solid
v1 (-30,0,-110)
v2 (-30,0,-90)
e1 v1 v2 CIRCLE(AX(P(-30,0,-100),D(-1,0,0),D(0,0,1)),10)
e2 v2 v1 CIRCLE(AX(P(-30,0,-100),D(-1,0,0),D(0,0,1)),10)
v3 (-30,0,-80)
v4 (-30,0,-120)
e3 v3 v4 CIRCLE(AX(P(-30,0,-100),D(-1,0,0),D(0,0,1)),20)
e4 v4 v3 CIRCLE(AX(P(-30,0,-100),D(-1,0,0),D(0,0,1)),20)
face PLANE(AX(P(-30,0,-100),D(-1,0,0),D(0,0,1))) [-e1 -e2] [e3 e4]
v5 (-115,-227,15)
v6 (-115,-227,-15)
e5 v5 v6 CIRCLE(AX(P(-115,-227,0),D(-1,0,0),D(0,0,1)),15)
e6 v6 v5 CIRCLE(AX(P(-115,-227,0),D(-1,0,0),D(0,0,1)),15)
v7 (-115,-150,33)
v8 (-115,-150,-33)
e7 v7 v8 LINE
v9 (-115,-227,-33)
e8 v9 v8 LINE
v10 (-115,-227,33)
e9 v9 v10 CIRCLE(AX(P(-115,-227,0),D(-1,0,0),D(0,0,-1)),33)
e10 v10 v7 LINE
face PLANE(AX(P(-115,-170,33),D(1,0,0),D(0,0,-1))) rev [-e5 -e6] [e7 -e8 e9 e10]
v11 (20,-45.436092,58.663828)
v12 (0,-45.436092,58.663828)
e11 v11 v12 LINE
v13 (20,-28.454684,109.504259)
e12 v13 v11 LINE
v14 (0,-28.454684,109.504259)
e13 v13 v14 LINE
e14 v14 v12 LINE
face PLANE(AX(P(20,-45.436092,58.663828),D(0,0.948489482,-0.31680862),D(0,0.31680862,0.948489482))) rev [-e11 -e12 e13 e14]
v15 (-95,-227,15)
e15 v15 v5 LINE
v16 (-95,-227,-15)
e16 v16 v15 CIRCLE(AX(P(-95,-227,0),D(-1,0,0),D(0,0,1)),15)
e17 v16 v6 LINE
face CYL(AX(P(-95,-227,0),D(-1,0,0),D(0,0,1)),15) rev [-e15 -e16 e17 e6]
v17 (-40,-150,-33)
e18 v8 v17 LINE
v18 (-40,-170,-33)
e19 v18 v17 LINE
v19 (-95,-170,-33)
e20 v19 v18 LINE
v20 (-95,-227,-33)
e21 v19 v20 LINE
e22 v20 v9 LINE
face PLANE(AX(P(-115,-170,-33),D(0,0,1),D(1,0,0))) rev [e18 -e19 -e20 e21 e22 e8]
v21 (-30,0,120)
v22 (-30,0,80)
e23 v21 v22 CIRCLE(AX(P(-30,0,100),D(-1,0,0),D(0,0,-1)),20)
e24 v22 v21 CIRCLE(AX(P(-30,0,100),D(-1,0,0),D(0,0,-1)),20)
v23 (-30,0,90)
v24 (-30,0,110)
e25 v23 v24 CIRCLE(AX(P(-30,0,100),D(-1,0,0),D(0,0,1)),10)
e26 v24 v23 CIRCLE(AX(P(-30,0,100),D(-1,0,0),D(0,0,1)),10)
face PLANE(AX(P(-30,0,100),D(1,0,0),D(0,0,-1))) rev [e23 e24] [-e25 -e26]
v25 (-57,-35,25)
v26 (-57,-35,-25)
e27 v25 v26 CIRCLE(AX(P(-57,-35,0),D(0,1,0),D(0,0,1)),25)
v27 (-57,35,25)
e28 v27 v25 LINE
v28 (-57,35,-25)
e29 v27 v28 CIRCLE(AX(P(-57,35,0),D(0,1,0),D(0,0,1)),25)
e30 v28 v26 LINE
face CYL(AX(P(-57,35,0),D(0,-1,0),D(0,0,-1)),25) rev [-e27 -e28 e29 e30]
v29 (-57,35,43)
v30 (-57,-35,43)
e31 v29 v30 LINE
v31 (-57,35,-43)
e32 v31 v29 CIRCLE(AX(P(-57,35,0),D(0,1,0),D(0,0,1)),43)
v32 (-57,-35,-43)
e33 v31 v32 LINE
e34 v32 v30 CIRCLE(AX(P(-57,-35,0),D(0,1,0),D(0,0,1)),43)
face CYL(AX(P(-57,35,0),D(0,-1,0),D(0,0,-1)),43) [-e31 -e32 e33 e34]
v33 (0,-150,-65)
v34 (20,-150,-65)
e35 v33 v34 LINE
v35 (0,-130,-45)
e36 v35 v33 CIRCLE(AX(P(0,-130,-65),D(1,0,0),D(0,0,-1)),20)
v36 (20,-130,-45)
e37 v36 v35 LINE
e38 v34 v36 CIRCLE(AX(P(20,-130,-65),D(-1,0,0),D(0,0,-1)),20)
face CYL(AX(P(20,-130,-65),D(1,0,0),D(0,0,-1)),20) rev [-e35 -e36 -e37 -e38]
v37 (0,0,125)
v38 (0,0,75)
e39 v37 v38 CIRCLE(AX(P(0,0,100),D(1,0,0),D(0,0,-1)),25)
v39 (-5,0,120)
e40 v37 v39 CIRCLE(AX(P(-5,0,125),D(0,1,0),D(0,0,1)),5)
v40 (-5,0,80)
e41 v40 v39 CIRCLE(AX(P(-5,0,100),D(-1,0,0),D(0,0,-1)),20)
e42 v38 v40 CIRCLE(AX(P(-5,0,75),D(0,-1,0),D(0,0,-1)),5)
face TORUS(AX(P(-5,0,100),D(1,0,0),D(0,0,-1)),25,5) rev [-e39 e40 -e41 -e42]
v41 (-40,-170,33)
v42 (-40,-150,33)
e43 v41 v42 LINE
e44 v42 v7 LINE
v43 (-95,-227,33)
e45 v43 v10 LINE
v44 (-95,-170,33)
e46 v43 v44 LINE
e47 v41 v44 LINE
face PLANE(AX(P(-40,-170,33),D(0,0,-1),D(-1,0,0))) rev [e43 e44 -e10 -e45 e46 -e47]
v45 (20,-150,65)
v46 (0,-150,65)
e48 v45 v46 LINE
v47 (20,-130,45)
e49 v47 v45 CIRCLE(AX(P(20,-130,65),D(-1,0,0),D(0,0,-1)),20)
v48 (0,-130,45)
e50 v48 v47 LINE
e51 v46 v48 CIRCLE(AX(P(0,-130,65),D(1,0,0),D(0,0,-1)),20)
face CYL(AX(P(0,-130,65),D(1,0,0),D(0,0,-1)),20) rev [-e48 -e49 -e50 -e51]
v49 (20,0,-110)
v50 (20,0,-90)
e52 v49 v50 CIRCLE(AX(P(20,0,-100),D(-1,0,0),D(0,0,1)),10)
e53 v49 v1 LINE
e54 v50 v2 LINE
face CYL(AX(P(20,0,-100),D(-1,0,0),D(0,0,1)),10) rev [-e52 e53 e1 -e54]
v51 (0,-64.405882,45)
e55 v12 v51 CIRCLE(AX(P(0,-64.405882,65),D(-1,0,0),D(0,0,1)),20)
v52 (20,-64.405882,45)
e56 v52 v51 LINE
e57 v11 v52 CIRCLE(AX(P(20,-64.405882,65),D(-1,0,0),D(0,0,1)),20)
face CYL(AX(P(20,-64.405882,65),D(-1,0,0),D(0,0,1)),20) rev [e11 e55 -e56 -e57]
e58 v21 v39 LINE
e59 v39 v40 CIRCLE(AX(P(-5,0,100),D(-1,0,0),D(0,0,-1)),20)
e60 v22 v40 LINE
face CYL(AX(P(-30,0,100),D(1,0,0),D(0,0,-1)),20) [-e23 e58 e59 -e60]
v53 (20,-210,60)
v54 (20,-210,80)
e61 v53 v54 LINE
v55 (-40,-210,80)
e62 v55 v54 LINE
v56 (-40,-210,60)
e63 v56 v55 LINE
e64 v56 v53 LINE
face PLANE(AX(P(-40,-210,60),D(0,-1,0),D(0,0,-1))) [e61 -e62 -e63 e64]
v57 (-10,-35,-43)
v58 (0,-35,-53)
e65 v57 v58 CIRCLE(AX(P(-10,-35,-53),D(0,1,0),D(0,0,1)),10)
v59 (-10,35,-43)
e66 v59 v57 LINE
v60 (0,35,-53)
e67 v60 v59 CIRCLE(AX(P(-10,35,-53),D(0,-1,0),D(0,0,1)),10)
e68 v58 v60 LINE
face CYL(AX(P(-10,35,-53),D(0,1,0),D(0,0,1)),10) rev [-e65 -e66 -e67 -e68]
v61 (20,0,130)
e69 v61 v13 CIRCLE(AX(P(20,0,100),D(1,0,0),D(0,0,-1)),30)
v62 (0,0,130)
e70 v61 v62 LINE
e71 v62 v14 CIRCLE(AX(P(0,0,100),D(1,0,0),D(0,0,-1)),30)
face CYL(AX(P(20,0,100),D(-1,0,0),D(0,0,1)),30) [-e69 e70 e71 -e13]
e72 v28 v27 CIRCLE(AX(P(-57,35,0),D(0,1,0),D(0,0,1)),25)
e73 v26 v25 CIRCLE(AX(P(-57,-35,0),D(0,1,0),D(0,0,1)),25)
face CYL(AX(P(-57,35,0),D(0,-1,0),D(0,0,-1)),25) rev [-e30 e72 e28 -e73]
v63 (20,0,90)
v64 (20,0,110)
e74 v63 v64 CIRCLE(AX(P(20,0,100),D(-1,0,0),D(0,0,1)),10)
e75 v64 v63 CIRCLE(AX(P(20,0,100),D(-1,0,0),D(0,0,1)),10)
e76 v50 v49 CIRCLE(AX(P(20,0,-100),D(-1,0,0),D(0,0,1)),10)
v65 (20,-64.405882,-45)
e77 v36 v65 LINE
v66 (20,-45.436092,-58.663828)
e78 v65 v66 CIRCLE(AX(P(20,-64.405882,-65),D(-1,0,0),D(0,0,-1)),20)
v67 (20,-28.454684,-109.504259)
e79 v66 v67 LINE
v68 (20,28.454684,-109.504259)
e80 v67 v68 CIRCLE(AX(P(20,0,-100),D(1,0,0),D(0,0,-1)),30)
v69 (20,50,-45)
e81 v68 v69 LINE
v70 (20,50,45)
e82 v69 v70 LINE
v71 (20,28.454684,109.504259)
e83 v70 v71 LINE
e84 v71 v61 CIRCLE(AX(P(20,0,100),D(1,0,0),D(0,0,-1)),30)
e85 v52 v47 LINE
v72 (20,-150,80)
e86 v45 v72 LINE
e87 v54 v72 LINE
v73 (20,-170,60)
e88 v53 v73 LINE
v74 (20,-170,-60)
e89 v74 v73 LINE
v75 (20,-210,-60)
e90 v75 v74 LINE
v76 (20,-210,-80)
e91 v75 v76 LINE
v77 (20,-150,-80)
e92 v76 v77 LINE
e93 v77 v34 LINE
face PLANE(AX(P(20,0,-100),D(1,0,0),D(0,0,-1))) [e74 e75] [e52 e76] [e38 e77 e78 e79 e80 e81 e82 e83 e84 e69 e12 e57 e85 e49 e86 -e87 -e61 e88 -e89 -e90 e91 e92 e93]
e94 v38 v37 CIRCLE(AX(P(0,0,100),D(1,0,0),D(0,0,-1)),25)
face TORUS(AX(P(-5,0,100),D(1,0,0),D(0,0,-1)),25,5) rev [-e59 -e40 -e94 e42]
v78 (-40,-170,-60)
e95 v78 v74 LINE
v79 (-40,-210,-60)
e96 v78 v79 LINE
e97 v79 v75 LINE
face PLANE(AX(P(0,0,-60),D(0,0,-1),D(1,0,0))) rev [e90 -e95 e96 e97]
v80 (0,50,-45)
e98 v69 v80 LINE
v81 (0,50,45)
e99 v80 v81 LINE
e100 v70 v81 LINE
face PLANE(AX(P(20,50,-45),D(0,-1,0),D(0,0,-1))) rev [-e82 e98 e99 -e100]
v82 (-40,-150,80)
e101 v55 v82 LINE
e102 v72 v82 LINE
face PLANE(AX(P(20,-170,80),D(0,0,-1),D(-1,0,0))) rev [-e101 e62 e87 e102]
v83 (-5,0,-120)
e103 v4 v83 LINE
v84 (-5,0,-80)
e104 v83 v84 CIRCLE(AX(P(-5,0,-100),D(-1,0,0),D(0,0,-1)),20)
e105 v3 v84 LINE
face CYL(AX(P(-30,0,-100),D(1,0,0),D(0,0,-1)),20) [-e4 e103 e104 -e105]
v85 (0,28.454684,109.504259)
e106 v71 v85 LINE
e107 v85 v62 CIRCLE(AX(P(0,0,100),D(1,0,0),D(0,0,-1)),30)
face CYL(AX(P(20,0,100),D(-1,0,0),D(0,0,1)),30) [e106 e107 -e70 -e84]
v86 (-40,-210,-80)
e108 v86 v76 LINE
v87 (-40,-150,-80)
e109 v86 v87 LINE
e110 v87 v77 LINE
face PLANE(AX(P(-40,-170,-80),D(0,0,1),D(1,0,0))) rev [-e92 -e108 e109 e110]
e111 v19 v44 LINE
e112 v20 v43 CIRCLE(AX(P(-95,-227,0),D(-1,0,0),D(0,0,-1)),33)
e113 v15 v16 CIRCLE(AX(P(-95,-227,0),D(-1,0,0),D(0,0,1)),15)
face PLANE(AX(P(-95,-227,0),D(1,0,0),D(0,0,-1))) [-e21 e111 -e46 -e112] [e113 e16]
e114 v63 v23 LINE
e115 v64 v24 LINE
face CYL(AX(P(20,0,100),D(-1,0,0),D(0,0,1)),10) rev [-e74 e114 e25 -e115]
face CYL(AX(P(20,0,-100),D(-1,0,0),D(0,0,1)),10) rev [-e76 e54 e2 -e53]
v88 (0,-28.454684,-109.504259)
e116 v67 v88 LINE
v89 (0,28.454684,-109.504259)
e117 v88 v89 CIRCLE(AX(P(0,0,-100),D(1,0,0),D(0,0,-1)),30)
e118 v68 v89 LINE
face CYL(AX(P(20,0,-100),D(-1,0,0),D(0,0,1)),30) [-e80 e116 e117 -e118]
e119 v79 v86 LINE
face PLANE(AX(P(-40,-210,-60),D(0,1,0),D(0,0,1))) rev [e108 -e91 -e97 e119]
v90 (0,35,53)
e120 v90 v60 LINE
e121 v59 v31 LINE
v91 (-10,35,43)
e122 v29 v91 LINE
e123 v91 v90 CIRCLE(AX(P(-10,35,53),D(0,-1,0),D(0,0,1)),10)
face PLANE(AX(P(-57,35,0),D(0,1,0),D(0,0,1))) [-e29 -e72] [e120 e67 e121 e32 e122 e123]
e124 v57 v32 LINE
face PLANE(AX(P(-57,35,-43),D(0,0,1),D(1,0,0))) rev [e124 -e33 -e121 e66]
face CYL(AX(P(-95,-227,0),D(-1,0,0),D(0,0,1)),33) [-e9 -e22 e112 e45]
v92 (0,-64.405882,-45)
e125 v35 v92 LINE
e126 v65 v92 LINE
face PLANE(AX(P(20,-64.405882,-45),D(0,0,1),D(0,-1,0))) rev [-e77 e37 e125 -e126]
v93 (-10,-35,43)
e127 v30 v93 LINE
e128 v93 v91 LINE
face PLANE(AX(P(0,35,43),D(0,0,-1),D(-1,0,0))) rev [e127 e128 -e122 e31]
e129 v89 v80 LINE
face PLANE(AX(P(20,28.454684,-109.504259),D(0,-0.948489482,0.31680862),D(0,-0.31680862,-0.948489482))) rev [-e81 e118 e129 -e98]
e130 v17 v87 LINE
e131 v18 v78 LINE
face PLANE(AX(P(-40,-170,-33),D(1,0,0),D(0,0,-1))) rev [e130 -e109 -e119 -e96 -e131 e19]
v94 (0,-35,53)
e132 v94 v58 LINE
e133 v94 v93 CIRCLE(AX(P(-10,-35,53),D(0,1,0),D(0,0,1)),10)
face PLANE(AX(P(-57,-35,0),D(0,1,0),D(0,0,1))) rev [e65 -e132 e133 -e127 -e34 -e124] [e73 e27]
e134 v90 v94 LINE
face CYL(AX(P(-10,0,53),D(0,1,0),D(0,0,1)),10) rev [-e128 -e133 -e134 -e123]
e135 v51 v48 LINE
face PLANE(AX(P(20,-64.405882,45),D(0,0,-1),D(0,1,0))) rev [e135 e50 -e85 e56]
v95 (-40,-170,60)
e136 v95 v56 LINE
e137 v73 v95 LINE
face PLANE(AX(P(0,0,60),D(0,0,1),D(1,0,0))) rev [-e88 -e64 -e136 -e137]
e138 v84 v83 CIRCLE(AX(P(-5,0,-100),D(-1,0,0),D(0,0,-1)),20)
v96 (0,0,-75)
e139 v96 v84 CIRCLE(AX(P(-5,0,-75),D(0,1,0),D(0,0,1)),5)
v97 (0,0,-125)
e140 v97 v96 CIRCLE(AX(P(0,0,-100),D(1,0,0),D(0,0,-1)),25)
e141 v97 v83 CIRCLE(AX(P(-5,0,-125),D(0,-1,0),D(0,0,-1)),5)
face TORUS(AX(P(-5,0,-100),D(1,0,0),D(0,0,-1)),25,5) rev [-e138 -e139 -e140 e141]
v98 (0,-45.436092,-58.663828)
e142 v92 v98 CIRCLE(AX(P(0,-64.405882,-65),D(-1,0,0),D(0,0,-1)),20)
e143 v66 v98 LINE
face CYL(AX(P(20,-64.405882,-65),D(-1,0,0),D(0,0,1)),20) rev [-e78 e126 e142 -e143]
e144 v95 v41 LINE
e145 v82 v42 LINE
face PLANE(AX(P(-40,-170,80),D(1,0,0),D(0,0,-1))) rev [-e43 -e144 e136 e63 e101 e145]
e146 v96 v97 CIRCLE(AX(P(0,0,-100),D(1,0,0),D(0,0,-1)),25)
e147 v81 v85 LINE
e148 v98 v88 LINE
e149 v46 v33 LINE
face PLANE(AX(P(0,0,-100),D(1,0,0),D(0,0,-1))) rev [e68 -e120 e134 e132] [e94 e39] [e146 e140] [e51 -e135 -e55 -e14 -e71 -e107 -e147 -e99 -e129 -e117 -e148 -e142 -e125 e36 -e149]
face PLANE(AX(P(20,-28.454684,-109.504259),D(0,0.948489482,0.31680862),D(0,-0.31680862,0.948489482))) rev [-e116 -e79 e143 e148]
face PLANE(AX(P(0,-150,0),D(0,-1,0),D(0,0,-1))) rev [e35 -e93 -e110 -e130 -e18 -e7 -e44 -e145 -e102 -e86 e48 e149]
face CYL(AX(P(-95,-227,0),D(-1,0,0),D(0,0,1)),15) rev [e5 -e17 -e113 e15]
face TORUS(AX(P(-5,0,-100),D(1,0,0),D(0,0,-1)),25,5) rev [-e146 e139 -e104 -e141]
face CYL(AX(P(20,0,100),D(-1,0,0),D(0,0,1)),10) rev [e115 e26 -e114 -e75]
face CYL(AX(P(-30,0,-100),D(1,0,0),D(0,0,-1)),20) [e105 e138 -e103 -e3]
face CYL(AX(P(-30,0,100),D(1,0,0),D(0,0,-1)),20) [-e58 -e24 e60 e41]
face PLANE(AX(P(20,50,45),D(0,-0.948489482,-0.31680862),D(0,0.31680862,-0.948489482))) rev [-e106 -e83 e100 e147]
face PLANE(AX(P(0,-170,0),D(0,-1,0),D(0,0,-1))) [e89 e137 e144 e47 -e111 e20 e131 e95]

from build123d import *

# Parameters (mm, degrees)
BASE_BODY_DEPTH          = 20
HUB_BOSS_SKETCH_R        = 20
HUB_BOSS_DEPTH           = 30
HUB_BORE_SKETCH_R        = 10
HUB_BORE_20_DEPTH        = 205.694894905
FOOT_BLOCK_SKETCH_R      = 25
FOOT_BLOCK_DEPTH         = 35
HINGE_PLATE_DEPTH        = 20
PLATE_STIFFENER_SKETCH_R = 15
PLATE_STIFFENER_DEPTH    = 20
PIN_BOSS_SKETCH_W        = 60
PIN_BOSS_SKETCH_H        = 60
PIN_BOSS_DEPTH           = 20
HUB_FILLET_R5_R          = 5
FOOT_BLOCK_FILLET_R10_R  = 10
HINGE_PLATE_FILLET_R20_R = 20


with BuildPart() as part:
    # Base Profile Sketch → Base Body (new body)
    with BuildSketch(Plane(origin=(0, 0, 0), x_dir=(0, 0, -1), z_dir=(1, 0, 0))):
        with BuildLine():
            Line((45, 50), (-45, 50))
            Line((-45, 50), (-109.504258609, 28.45468447))
            ThreePointArc((-109.504258609, 28.45468447), (-130, 0), (-109.504258609, -28.45468447))
            Line((-109.504258609, -28.45468447), (-58.663827594, -45.436092388))
            ThreePointArc((-58.663827594, -45.436092388), (-48.771576661, -52.716644423), (-45, -64.405882035))
            Line((-45, -64.405882035), (-45, -150))
            Line((-45, -150), (45, -150))
            Line((45, -150), (45, -64.405882035))
            ThreePointArc((45, -64.405882035), (48.771576661, -52.716644423), (58.663827594, -45.436092388))
            Line((58.663827594, -45.436092388), (109.504258609, -28.45468447))
            ThreePointArc((109.504258609, -28.45468447), (130, 0), (109.504258609, 28.45468447))
            Line((109.504258609, 28.45468447), (45, 50))
        make_face()
    extrude(amount=BASE_BODY_DEPTH)

    # Hub Boss Sketch → Hub Boss (add)
    with BuildSketch(Plane.ZY):
        with Locations(Location((-100, 0, 0), (0, 0, 180))):
            Circle(HUB_BOSS_SKETCH_R)
        with Locations(Location((100, 0, 0), (0, 0, 180))):
            Circle(HUB_BOSS_SKETCH_R)
    extrude(amount=HUB_BOSS_DEPTH)

    # Hub Bore Sketch → Hub Bore Ø20 (cut, through all)
    with BuildSketch(Plane.ZY.offset(30)):
        with Locations((-100, 0)):
            Circle(HUB_BORE_SKETCH_R)
        with Locations((100, 0)):
            Circle(HUB_BORE_SKETCH_R)
    extrude(amount=-HUB_BORE_20_DEPTH, mode=Mode.SUBTRACT)

    # Foot Block Sketch → Foot Block (add, symmetric)
    with BuildSketch(Plane(origin=(0, 0, 0), x_dir=(1, 0, 0), z_dir=(0, 1, 0))):
        with BuildLine():
            Line((-57, 43), (0, 43))
            Line((0, 43), (0, -43))
            Line((0, -43), (-57, -43))
            ThreePointArc((-57, -43), (-100, 0), (-57, 43))
        make_face()
        with Locations(Location((-57, 0, 0), (0, 0, 270))):
            Circle(FOOT_BLOCK_SKETCH_R, mode=Mode.SUBTRACT)
    extrude(amount=FOOT_BLOCK_DEPTH, both=True)

    # Hinge Plate Sketch → Hinge Plate (add)
    with BuildSketch(Plane.XZ.offset(150)):
        Polygon((20, 0), (20, 80), (-40, 80), (-40, 33), (-115, 33), (-115, -33), (-40, -33), (-40, -80), (20, -80), align=None)
    extrude(amount=HINGE_PLATE_DEPTH)

    # Plate Stiffener Sketch → Plate Stiffener (add)
    with BuildSketch(Plane.ZY.offset(115)):
        with BuildLine():
            Line((-33, -150), (33, -150))
            Line((33, -150), (33, -227))
            ThreePointArc((33, -227), (0, -260), (-33, -227))
            Line((-33, -227), (-33, -150))
        make_face()
        with Locations((0, -227)):
            Circle(PLATE_STIFFENER_SKETCH_R, mode=Mode.SUBTRACT)
    extrude(amount=-PLATE_STIFFENER_DEPTH)

    # Pin Boss Sketch → Pin Boss (add)
    with BuildSketch(Plane.XY.offset(80)):
        with Locations((-10, -180)):
            Rectangle(PIN_BOSS_SKETCH_W, PIN_BOSS_SKETCH_H)
    pin_boss = extrude(amount=-PIN_BOSS_DEPTH)

    # Pin Boss Mirror: Pin Boss across plane
    add(pin_boss.mirror(Plane.XY))

    # Hub Fillet R5
    hub_fillet_r5_edges = [part.edges().sort_by_distance(p)[0] for p in [
        (0, 0, -80),
        (0, 0, 120),
    ]]
    fillet(hub_fillet_r5_edges, radius=HUB_FILLET_R5_R)

    # Foot Block Fillet R10
    foot_block_fillet_r10_edges = [part.edges().sort_by_distance(p)[0] for p in [
        (0, 0, 43),
        (0, 0, -43),
    ]]
    fillet(foot_block_fillet_r10_edges, radius=FOOT_BLOCK_FILLET_R10_R)

    # Hinge Plate Fillet R20
    hinge_plate_fillet_r20_edges = [part.edges().sort_by_distance(p)[0] for p in [
        (10, -150, -45),
        (10, -150, 45),
    ]]
    fillet(hinge_plate_fillet_r20_edges, radius=HINGE_PLATE_FILLET_R20_R)


solid = part.part
